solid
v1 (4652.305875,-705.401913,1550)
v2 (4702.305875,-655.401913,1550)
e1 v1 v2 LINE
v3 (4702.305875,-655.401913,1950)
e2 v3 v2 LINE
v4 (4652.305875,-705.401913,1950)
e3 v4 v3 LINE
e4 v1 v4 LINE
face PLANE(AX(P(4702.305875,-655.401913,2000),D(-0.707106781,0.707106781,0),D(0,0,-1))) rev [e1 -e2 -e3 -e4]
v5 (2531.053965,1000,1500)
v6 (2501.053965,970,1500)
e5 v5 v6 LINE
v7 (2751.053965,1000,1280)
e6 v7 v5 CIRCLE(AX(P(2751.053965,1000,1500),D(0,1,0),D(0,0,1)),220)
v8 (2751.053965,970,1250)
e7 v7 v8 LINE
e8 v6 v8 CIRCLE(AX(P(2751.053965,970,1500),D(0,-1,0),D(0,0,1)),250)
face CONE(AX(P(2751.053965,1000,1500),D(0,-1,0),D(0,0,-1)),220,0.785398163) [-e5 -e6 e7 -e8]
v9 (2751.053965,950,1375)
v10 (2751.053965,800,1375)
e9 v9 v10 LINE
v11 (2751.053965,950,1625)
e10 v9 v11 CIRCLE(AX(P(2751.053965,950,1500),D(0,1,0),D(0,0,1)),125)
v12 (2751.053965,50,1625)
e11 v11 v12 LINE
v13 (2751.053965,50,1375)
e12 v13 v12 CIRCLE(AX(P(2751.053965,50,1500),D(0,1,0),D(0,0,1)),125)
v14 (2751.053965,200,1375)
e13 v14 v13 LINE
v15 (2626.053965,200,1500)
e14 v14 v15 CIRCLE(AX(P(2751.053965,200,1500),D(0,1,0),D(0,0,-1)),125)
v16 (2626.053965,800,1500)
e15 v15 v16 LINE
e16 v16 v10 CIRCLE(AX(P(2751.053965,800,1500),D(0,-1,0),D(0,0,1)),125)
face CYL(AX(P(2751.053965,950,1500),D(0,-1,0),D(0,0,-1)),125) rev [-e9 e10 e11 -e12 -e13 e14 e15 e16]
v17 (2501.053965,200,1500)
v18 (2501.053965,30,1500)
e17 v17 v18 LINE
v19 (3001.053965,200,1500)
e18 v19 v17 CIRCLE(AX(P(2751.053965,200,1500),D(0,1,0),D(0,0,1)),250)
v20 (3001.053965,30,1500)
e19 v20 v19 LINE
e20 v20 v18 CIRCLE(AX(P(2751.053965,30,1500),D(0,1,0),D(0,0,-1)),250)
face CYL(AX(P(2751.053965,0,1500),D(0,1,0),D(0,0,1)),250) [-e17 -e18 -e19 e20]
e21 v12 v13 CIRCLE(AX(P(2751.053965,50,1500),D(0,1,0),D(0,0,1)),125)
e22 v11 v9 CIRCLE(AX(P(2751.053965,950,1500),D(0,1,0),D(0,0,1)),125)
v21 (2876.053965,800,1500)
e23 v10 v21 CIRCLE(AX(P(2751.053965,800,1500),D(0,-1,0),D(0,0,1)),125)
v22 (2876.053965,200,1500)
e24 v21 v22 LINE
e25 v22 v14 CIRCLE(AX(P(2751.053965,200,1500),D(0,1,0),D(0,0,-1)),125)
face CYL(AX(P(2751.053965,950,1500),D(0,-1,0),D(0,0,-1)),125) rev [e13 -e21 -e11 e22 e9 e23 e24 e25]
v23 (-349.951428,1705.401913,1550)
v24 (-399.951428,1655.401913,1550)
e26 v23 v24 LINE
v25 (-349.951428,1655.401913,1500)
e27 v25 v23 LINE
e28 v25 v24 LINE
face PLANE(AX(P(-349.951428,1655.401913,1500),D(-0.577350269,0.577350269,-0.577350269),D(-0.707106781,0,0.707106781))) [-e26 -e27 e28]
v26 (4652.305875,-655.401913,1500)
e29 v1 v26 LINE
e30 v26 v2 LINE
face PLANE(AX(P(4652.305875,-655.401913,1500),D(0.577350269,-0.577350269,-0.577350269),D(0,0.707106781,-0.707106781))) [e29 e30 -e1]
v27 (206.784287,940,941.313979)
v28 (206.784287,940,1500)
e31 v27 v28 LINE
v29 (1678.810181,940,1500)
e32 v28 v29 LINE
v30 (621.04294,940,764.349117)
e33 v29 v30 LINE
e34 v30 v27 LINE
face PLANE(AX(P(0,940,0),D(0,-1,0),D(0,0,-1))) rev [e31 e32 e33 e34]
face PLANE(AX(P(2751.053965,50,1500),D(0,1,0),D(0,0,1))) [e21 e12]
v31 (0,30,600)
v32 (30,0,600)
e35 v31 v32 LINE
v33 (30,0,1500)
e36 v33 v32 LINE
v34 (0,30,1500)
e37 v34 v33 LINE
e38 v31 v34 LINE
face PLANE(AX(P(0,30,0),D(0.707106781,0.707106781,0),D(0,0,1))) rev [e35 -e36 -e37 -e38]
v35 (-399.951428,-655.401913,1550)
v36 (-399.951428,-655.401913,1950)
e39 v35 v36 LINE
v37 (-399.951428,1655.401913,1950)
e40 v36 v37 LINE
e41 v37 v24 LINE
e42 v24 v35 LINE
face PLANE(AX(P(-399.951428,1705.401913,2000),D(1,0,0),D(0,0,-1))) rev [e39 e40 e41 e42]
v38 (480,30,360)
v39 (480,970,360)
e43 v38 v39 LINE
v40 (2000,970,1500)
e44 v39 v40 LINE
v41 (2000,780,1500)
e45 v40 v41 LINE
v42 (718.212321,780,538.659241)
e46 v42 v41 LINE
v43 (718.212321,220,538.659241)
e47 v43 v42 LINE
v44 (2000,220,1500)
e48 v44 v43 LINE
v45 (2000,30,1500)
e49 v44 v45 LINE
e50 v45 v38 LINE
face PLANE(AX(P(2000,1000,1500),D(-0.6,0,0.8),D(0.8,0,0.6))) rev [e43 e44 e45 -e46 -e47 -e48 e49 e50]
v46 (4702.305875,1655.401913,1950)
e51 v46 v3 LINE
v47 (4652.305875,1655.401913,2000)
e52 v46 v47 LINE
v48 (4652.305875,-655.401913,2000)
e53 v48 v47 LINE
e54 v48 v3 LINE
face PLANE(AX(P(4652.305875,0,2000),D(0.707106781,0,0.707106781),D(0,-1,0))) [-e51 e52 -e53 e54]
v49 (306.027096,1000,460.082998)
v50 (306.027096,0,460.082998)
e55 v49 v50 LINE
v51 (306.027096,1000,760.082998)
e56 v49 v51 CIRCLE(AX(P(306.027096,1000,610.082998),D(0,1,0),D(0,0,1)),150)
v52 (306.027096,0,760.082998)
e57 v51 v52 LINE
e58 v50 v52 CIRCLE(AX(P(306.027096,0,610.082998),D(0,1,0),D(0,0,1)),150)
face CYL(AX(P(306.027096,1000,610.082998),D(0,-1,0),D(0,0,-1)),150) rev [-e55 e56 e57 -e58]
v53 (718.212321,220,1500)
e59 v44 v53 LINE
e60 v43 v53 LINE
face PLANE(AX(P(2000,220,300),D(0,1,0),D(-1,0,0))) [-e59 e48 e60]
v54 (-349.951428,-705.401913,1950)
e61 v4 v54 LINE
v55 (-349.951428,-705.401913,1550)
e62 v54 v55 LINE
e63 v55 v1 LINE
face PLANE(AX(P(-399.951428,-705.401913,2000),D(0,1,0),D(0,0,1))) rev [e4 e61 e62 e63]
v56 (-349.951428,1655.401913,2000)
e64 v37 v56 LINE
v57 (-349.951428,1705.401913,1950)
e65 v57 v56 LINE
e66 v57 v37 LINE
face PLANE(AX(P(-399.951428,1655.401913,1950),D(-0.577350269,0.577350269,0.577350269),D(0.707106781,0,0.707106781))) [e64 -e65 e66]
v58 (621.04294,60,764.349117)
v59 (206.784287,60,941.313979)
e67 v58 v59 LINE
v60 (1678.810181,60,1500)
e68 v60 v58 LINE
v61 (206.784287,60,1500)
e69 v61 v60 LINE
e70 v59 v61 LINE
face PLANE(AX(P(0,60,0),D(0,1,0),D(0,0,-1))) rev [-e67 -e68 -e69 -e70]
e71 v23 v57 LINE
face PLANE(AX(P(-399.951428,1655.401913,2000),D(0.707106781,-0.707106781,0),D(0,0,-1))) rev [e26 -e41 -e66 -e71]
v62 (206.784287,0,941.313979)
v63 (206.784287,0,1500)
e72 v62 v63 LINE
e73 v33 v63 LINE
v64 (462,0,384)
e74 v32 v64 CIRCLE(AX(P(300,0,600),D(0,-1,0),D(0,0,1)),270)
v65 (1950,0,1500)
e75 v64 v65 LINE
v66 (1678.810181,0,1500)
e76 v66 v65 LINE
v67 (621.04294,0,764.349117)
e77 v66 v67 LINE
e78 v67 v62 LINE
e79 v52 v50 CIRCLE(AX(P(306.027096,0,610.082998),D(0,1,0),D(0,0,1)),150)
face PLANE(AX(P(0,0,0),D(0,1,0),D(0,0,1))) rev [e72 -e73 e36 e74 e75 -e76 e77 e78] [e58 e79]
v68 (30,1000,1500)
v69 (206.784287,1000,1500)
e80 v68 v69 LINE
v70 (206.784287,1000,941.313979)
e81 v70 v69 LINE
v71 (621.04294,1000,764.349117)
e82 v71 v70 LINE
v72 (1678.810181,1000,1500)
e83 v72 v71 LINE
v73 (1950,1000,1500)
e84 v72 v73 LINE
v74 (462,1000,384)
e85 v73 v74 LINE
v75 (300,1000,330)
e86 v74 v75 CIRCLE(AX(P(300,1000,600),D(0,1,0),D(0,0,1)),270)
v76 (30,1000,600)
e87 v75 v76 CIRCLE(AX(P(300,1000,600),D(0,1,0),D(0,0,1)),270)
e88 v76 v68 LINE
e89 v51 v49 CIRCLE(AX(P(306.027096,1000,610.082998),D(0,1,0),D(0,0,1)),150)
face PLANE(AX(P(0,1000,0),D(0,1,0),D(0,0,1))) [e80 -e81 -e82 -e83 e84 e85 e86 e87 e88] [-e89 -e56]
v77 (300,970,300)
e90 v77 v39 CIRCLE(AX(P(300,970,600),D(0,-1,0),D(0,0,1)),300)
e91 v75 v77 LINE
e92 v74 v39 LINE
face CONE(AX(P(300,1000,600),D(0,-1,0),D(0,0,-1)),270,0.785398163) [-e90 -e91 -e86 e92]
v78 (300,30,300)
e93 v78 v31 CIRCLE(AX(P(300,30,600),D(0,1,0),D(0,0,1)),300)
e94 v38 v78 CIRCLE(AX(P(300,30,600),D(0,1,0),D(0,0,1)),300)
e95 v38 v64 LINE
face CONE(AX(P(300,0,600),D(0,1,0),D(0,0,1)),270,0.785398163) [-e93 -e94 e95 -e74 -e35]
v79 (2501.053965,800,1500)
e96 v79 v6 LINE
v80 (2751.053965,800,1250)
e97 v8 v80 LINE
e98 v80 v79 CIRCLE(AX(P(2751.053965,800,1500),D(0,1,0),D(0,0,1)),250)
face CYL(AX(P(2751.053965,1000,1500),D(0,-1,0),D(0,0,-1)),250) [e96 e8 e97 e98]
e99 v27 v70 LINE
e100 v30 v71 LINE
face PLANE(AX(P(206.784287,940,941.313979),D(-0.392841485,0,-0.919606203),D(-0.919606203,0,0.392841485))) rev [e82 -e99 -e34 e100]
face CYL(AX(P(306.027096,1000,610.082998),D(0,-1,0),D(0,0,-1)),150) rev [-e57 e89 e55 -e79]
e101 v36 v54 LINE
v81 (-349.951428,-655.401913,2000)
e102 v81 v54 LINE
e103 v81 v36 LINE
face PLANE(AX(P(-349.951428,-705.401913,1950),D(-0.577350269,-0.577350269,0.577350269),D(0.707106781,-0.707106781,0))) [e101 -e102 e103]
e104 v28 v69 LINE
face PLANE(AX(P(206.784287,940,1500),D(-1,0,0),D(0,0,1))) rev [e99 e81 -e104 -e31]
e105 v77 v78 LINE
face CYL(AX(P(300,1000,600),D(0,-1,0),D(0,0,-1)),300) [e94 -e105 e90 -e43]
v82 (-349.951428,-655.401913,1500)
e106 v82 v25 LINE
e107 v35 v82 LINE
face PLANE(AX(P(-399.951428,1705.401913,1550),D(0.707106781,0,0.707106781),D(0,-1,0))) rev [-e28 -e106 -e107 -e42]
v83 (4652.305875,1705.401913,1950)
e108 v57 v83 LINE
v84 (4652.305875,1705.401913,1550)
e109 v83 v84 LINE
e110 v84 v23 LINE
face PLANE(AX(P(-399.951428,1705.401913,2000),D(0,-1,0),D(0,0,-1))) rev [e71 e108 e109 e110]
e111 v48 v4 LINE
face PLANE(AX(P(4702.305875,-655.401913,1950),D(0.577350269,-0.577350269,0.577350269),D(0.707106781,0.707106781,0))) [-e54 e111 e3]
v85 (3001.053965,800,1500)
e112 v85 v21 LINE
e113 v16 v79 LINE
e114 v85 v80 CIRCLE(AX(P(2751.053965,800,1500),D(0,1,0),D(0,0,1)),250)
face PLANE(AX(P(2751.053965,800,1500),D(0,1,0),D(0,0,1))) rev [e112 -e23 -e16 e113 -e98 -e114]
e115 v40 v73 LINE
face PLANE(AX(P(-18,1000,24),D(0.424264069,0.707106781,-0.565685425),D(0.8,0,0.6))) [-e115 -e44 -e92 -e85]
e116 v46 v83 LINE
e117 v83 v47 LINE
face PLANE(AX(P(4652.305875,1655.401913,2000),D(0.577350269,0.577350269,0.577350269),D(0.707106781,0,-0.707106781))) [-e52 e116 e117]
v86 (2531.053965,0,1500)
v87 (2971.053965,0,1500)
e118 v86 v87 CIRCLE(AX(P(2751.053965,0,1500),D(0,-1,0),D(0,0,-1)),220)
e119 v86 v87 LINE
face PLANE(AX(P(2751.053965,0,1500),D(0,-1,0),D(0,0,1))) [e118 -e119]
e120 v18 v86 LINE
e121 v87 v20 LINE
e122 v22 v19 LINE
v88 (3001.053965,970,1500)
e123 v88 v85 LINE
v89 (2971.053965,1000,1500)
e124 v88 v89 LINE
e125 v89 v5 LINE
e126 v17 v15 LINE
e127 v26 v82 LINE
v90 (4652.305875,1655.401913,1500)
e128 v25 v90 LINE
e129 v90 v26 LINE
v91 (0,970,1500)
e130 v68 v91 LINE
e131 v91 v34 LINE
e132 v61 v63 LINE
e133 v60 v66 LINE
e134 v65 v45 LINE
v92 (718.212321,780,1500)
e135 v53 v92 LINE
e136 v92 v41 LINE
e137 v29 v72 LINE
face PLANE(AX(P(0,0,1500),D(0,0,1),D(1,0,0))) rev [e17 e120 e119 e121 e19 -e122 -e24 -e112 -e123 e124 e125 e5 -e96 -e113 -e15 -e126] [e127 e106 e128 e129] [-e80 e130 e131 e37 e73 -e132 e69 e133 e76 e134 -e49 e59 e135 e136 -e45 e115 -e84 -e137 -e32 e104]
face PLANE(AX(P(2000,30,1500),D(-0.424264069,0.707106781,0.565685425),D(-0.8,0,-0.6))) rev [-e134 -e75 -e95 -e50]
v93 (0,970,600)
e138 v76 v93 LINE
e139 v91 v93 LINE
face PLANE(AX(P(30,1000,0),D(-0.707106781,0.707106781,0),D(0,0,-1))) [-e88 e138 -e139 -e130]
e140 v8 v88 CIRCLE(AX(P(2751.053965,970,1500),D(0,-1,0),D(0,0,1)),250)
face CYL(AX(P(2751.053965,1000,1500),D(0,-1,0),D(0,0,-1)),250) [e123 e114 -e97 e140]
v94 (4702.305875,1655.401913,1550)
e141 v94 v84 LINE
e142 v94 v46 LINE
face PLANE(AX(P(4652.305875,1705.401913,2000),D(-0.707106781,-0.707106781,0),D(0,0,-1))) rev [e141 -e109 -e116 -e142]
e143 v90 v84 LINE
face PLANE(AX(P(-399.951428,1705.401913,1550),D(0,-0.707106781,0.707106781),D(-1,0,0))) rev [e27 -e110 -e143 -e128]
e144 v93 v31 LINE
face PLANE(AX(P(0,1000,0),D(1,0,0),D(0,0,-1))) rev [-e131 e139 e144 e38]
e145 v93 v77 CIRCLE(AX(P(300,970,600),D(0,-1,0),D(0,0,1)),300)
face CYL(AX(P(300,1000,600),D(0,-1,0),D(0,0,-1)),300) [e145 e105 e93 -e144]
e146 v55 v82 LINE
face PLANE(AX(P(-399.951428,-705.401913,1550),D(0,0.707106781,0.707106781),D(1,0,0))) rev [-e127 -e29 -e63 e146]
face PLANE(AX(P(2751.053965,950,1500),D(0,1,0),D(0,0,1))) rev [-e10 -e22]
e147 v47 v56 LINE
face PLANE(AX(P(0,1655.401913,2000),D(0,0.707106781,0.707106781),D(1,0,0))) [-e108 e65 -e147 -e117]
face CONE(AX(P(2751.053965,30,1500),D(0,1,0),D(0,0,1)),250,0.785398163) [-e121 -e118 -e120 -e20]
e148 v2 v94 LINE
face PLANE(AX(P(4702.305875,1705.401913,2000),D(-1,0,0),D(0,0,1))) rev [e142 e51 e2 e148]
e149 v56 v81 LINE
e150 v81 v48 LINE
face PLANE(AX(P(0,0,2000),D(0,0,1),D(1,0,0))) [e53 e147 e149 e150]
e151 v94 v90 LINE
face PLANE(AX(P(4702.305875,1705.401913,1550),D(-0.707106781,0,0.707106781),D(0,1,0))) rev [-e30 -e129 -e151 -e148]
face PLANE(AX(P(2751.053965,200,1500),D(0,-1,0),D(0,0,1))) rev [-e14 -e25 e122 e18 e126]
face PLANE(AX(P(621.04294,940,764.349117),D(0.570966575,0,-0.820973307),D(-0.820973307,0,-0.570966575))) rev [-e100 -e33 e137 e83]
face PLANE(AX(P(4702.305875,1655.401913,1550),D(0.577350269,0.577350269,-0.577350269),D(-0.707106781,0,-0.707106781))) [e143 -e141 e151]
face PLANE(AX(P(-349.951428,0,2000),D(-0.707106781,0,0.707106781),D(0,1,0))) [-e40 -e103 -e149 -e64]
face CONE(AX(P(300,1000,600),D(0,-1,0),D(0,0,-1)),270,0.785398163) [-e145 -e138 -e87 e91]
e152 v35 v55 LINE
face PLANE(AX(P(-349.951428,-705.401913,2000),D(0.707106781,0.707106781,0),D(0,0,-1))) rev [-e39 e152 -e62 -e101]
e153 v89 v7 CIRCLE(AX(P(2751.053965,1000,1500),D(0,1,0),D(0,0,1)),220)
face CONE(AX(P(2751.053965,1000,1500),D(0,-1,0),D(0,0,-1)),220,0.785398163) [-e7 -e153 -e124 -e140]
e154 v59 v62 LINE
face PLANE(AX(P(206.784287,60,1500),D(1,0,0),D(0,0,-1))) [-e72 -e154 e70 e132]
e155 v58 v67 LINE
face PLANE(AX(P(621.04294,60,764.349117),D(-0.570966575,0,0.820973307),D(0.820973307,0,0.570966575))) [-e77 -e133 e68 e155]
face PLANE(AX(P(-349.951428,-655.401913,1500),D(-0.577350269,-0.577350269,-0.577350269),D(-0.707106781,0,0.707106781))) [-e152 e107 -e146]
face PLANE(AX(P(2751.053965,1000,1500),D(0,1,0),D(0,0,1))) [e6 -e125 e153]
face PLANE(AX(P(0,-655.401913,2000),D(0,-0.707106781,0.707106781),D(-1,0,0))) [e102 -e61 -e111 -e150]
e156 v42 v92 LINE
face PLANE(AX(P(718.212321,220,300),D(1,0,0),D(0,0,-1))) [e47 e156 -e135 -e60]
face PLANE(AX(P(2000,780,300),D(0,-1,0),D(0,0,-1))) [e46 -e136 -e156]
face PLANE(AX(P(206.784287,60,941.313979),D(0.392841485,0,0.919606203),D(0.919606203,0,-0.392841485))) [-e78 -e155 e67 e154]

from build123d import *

# Parameters (mm, degrees)
SKETCH1_R               = 150
BOSS_EXTRUDE1_DEPTH     = 1000
FILLET2_R               = 300
SKETCH2_W               = 5102.2573033
SKETCH2_H               = 2410.803825692
BOSS_EXTRUDE2_DEPTH     = 500
SKETCH3_R               = 250
BOSS_EXTRUDE3_DEPTH     = 200
CUT_EXTRUDE1_DEPTH      = 750
CUT_EXTRUDE1_DEPTH_BACK = 150
SKETCH4_R               = 125
CHAMFER1_SIZE           = 30
CHAMFER2_SIZE           = 30
CUT_EXTRUDE3_DEPTH      = 60
CHAMFER3_SIZE           = 50
SKETCH7_W               = 1281.787678956
SKETCH7_H               = 560
CUT_EXTRUDE4_DEPTH      = 5144.935869353


with BuildPart() as part:
    # Sketch1 → Boss-Extrude1 (new body)
    with BuildSketch(Plane(origin=(0, 0, 0), x_dir=(1, 0, 0), z_dir=(0, 1, 0))):
        Polygon((0, 0), (0, -1500), (2000, -1500), align=None)
        with Locations(Location((306.027096019, -610.082997658, 0), (0, 0, 270))):
            Circle(SKETCH1_R, mode=Mode.SUBTRACT)
    extrude(amount=BOSS_EXTRUDE1_DEPTH)

    # Fillet2
    fillet2_edges = [part.edges().sort_by_distance(p)[0] for p in [
        (0, 500, 0),
    ]]
    fillet(fillet2_edges, radius=FILLET2_R)

    # Sketch2 → Boss-Extrude2 (add)
    with BuildSketch(Plane.XY.offset(1500)):
        with Locations((2151.177223521, 500)):
            Rectangle(SKETCH2_W, SKETCH2_H)
    extrude(amount=BOSS_EXTRUDE2_DEPTH)

    # Sketch3 → Boss-Extrude3 (add)
    with BuildSketch(Plane(origin=(0, 800, 0), x_dir=(1, 0, 0), z_dir=(0, 1, 0))):
        with Locations((2751.053965142, -1500)):
            Circle(SKETCH3_R)
    boss_extrude3 = extrude(amount=BOSS_EXTRUDE3_DEPTH)

    # Mirror1: Boss-Extrude3 across plane
    add(boss_extrude3.mirror(Plane.ZX.offset(500)))

    # Sketch4 → Cut-Extrude1 (cut, two sides: drawn at the far end of the back side and taken through both)
    with BuildSketch(Plane(origin=(0, 200, 0), x_dir=(1, 0, 0), z_dir=(0, 1, 0)).offset(-CUT_EXTRUDE1_DEPTH_BACK)):
        with Locations(Location((2751.053965142, -1500, 0), (0, 0, 270))):
            Circle(SKETCH4_R)
    extrude(amount=CUT_EXTRUDE1_DEPTH + CUT_EXTRUDE1_DEPTH_BACK, mode=Mode.SUBTRACT)

    # Chamfer1
    chamfer1_edges = [part.edges().sort_by_distance(p)[0] for p in [
        (2751.053965142, 1000, 1250),
        (2751.053965142, 0, 1250),
    ]]
    chamfer(chamfer1_edges, length=CHAMFER1_SIZE)

    # Chamfer2
    chamfer2_edges = [part.edges().sort_by_distance(p)[0] for p in [
        (0, 0, 1050),
        (0, 1000, 1050),
        (165.83592135, 0, 331.6718427),
        (165.83592135, 1000, 331.6718427),
        (1240, 0, 930),
        (1240, 1000, 930),
    ]]
    chamfer(chamfer2_edges, length=CHAMFER2_SIZE)

    # Sketch6 → Cut-Extrude3 (cut)
    with BuildSketch(Plane(origin=(0, 1000, 0), x_dir=(1, 0, 0), z_dir=(0, 1, 0))):
        Polygon((206.784286563, -1500), (206.784286563, -941.313978524), (621.042939875, -764.349116915), (1678.810180856, -1500), align=None)
    cut_extrude3 = extrude(amount=-CUT_EXTRUDE3_DEPTH, mode=Mode.SUBTRACT)

    # Mirror2: Cut-Extrude3 across plane
    add(cut_extrude3.mirror(Plane.ZX.offset(500)), mode=Mode.SUBTRACT)

    # Chamfer3
    chamfer3_edges = [part.edges().sort_by_distance(p)[0] for p in [
        (4702.305875171, 500, 1500),
        (4702.305875171, -705.401912846, 1750),
        (2151.177223521, 1705.401912846, 1500),
        (4702.305875171, 1705.401912846, 1750),
        (-399.951428129, 500, 1500),
        (-399.951428129, 1705.401912846, 1750),
        (2151.177223521, -705.401912846, 1500),
        (-399.951428129, -705.401912846, 1750),
        (4702.305875171, 500, 2000),
        (2151.177223521, 1705.401912846, 2000),
        (-399.951428129, 500, 2000),
        (2151.177223521, -705.401912846, 2000),
    ]]
    chamfer(chamfer3_edges, length=CHAMFER3_SIZE)

    # Sketch7 → Cut-Extrude4 (cut, through all)
    with BuildSketch(Plane(origin=(0, 0, 1500), x_dir=(-1, 0, 0), z_dir=(0, 0, -1))):
        with Locations((-1359.106160522, 500)):
            Rectangle(SKETCH7_W, SKETCH7_H)
    extrude(amount=CUT_EXTRUDE4_DEPTH, mode=Mode.SUBTRACT)


solid = part.part
